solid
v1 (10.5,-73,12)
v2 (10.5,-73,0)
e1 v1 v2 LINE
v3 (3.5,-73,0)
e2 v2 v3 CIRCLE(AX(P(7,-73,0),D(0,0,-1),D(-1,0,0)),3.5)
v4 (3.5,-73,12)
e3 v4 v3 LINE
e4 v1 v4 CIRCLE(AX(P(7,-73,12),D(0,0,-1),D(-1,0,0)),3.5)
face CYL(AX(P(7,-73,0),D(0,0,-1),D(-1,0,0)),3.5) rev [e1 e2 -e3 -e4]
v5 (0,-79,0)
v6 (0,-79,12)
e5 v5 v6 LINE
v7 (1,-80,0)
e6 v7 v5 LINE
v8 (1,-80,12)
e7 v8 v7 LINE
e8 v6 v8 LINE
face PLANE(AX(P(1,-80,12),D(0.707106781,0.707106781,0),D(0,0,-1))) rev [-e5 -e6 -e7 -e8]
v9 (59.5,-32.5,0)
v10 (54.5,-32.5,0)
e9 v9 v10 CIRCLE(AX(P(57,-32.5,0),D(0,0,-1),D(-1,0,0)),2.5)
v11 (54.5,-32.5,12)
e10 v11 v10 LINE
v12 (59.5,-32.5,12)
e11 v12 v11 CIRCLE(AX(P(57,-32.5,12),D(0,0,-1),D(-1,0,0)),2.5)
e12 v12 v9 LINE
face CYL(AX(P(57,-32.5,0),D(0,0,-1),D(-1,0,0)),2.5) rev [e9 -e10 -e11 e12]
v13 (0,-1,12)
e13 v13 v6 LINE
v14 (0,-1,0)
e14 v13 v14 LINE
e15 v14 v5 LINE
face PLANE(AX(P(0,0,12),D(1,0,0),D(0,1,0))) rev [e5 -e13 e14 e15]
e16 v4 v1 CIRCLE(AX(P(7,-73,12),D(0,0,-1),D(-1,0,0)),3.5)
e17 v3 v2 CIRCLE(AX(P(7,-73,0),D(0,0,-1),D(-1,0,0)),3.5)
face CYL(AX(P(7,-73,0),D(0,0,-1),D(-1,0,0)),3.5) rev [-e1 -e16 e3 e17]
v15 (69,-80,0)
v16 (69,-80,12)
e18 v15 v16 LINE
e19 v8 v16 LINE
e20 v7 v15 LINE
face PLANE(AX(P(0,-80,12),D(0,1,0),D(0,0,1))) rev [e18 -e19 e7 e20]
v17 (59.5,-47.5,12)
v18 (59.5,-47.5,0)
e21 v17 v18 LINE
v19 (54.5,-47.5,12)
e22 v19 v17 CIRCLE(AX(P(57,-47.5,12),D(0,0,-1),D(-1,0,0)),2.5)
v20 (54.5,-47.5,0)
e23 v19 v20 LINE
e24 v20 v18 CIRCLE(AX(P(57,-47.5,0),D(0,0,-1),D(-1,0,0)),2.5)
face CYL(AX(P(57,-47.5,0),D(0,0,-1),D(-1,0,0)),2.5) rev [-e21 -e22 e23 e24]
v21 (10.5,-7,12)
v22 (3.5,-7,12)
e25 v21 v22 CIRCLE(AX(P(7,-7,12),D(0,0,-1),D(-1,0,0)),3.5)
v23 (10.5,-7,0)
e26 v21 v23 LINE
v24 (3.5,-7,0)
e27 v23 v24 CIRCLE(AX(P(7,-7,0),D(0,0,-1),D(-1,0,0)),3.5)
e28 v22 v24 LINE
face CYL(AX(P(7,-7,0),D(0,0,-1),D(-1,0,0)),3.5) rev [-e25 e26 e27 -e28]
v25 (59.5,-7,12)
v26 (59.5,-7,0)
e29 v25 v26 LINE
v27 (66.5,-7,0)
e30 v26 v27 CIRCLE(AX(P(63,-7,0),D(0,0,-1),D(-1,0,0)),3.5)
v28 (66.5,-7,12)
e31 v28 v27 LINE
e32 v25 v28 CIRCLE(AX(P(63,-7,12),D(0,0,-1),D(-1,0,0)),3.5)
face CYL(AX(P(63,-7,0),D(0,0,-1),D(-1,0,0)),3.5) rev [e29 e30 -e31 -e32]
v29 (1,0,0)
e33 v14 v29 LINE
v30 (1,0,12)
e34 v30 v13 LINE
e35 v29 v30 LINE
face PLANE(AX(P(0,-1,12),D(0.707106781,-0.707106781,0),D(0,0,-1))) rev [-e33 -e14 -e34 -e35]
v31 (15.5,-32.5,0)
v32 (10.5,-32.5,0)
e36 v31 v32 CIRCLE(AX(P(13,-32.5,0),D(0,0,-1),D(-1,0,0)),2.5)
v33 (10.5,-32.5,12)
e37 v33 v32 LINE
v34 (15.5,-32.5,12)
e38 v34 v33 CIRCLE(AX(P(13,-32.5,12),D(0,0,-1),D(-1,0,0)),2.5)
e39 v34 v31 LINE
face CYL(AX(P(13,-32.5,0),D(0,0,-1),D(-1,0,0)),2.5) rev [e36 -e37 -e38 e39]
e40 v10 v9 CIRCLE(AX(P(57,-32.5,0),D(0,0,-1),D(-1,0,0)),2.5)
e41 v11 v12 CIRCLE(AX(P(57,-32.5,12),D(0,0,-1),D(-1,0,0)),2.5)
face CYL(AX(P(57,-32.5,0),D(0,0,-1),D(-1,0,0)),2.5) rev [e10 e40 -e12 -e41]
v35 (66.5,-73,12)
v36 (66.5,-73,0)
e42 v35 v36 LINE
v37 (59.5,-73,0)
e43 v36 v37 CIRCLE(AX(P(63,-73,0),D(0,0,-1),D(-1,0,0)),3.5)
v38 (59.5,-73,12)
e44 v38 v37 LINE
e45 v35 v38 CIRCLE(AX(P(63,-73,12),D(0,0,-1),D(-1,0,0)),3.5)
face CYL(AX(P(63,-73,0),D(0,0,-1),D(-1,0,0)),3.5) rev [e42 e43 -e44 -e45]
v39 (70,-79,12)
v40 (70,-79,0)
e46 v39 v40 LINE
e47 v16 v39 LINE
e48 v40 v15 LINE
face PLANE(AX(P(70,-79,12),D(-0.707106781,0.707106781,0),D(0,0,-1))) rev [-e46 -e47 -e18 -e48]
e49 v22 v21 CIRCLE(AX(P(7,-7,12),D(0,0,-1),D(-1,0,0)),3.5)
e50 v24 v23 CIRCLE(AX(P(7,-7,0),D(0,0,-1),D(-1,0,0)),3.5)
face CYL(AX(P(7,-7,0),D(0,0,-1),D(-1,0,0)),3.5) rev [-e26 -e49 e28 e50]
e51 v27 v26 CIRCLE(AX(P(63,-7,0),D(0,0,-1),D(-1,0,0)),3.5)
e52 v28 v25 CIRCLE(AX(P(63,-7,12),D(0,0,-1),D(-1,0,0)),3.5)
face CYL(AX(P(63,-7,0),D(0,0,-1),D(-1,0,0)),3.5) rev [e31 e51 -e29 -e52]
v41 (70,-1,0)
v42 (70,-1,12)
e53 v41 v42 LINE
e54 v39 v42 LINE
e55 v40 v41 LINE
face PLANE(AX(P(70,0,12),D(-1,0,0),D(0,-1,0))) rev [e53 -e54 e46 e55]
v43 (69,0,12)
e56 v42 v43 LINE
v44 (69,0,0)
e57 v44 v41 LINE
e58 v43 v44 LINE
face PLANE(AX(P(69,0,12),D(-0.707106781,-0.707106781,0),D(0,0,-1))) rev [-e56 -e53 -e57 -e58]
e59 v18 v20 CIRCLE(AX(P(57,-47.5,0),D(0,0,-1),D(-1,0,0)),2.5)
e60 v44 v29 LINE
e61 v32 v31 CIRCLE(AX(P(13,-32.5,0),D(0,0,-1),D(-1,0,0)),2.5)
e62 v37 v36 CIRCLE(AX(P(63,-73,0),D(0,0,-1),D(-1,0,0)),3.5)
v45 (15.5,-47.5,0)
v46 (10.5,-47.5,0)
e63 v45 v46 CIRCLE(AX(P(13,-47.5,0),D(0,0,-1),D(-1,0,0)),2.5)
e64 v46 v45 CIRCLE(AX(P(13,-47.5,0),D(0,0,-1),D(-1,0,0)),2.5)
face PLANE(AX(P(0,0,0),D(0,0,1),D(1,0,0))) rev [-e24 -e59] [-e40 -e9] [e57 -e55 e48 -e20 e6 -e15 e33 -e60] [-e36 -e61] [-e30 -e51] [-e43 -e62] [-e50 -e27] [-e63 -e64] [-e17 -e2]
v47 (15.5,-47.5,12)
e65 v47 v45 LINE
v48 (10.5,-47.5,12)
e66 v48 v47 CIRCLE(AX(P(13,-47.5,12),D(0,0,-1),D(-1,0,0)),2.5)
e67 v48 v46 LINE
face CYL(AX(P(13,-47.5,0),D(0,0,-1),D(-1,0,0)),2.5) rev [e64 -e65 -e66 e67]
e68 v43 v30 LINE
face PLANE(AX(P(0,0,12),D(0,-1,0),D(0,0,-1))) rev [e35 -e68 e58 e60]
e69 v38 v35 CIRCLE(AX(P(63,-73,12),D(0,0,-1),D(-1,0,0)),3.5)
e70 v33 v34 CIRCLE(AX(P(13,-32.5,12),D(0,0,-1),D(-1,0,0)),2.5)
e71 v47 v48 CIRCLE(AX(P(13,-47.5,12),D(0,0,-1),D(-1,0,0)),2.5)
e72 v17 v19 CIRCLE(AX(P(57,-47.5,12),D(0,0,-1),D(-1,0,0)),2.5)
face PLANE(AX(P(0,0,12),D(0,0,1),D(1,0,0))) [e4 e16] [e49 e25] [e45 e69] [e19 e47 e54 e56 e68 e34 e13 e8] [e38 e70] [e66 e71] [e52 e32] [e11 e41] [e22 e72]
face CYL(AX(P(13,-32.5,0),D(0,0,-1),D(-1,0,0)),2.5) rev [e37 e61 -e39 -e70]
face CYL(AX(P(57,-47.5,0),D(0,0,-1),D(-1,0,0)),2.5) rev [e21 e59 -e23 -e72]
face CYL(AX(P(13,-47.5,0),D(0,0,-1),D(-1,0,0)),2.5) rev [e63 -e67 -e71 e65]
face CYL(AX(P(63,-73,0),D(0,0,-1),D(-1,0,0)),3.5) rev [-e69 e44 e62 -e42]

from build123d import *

# Parameters (mm, degrees)
SKETCH_1_W            = 70
SKETCH_1_H            = 80
EXTRUDE_1_DEPTH       = 12
CHAMFER_1_SIZE        = 1
HOLE_WIZARD_7_0_7_1_D = 7
HOLE_WIZARD_M6_1_D    = 5


with BuildPart() as part:
    # 草图1 → 凸台-拉伸1 (new body)
    with BuildSketch(Plane.XY):
        with Locations((35, -40)):
            Rectangle(SKETCH_1_W, SKETCH_1_H)
    extrude(amount=EXTRUDE_1_DEPTH)

    # 倒角1
    chamfer_1_edges = [part.edges().sort_by_distance(p)[0] for p in [
        (0, 0, 6),
        (70, 0, 6),
        (70, -80, 6),
        (0, -80, 6),
    ]]
    chamfer(chamfer_1_edges, length=CHAMFER_1_SIZE)

    # Ø7.0 (7) 直径孔1 (through all)
    with Locations(Plane(origin=(0, 0, 0), x_dir=(-1, 0, 0), z_dir=(0, 0, -1))):
        with Locations((-7, -73), (-7, -7), (-63, -73), (-63, -7)):
            Hole(HOLE_WIZARD_7_0_7_1_D / 2)

    # M6 螺纹孔1 (through all)
    with Locations(Plane(origin=(0, 0, 0), x_dir=(-1, 0, 0), z_dir=(0, 0, -1))):
        with Locations((-57, -32.5), (-57, -47.5), (-13, -47.5), (-13, -32.5)):
            Hole(HOLE_WIZARD_M6_1_D / 2)


solid = part.part
